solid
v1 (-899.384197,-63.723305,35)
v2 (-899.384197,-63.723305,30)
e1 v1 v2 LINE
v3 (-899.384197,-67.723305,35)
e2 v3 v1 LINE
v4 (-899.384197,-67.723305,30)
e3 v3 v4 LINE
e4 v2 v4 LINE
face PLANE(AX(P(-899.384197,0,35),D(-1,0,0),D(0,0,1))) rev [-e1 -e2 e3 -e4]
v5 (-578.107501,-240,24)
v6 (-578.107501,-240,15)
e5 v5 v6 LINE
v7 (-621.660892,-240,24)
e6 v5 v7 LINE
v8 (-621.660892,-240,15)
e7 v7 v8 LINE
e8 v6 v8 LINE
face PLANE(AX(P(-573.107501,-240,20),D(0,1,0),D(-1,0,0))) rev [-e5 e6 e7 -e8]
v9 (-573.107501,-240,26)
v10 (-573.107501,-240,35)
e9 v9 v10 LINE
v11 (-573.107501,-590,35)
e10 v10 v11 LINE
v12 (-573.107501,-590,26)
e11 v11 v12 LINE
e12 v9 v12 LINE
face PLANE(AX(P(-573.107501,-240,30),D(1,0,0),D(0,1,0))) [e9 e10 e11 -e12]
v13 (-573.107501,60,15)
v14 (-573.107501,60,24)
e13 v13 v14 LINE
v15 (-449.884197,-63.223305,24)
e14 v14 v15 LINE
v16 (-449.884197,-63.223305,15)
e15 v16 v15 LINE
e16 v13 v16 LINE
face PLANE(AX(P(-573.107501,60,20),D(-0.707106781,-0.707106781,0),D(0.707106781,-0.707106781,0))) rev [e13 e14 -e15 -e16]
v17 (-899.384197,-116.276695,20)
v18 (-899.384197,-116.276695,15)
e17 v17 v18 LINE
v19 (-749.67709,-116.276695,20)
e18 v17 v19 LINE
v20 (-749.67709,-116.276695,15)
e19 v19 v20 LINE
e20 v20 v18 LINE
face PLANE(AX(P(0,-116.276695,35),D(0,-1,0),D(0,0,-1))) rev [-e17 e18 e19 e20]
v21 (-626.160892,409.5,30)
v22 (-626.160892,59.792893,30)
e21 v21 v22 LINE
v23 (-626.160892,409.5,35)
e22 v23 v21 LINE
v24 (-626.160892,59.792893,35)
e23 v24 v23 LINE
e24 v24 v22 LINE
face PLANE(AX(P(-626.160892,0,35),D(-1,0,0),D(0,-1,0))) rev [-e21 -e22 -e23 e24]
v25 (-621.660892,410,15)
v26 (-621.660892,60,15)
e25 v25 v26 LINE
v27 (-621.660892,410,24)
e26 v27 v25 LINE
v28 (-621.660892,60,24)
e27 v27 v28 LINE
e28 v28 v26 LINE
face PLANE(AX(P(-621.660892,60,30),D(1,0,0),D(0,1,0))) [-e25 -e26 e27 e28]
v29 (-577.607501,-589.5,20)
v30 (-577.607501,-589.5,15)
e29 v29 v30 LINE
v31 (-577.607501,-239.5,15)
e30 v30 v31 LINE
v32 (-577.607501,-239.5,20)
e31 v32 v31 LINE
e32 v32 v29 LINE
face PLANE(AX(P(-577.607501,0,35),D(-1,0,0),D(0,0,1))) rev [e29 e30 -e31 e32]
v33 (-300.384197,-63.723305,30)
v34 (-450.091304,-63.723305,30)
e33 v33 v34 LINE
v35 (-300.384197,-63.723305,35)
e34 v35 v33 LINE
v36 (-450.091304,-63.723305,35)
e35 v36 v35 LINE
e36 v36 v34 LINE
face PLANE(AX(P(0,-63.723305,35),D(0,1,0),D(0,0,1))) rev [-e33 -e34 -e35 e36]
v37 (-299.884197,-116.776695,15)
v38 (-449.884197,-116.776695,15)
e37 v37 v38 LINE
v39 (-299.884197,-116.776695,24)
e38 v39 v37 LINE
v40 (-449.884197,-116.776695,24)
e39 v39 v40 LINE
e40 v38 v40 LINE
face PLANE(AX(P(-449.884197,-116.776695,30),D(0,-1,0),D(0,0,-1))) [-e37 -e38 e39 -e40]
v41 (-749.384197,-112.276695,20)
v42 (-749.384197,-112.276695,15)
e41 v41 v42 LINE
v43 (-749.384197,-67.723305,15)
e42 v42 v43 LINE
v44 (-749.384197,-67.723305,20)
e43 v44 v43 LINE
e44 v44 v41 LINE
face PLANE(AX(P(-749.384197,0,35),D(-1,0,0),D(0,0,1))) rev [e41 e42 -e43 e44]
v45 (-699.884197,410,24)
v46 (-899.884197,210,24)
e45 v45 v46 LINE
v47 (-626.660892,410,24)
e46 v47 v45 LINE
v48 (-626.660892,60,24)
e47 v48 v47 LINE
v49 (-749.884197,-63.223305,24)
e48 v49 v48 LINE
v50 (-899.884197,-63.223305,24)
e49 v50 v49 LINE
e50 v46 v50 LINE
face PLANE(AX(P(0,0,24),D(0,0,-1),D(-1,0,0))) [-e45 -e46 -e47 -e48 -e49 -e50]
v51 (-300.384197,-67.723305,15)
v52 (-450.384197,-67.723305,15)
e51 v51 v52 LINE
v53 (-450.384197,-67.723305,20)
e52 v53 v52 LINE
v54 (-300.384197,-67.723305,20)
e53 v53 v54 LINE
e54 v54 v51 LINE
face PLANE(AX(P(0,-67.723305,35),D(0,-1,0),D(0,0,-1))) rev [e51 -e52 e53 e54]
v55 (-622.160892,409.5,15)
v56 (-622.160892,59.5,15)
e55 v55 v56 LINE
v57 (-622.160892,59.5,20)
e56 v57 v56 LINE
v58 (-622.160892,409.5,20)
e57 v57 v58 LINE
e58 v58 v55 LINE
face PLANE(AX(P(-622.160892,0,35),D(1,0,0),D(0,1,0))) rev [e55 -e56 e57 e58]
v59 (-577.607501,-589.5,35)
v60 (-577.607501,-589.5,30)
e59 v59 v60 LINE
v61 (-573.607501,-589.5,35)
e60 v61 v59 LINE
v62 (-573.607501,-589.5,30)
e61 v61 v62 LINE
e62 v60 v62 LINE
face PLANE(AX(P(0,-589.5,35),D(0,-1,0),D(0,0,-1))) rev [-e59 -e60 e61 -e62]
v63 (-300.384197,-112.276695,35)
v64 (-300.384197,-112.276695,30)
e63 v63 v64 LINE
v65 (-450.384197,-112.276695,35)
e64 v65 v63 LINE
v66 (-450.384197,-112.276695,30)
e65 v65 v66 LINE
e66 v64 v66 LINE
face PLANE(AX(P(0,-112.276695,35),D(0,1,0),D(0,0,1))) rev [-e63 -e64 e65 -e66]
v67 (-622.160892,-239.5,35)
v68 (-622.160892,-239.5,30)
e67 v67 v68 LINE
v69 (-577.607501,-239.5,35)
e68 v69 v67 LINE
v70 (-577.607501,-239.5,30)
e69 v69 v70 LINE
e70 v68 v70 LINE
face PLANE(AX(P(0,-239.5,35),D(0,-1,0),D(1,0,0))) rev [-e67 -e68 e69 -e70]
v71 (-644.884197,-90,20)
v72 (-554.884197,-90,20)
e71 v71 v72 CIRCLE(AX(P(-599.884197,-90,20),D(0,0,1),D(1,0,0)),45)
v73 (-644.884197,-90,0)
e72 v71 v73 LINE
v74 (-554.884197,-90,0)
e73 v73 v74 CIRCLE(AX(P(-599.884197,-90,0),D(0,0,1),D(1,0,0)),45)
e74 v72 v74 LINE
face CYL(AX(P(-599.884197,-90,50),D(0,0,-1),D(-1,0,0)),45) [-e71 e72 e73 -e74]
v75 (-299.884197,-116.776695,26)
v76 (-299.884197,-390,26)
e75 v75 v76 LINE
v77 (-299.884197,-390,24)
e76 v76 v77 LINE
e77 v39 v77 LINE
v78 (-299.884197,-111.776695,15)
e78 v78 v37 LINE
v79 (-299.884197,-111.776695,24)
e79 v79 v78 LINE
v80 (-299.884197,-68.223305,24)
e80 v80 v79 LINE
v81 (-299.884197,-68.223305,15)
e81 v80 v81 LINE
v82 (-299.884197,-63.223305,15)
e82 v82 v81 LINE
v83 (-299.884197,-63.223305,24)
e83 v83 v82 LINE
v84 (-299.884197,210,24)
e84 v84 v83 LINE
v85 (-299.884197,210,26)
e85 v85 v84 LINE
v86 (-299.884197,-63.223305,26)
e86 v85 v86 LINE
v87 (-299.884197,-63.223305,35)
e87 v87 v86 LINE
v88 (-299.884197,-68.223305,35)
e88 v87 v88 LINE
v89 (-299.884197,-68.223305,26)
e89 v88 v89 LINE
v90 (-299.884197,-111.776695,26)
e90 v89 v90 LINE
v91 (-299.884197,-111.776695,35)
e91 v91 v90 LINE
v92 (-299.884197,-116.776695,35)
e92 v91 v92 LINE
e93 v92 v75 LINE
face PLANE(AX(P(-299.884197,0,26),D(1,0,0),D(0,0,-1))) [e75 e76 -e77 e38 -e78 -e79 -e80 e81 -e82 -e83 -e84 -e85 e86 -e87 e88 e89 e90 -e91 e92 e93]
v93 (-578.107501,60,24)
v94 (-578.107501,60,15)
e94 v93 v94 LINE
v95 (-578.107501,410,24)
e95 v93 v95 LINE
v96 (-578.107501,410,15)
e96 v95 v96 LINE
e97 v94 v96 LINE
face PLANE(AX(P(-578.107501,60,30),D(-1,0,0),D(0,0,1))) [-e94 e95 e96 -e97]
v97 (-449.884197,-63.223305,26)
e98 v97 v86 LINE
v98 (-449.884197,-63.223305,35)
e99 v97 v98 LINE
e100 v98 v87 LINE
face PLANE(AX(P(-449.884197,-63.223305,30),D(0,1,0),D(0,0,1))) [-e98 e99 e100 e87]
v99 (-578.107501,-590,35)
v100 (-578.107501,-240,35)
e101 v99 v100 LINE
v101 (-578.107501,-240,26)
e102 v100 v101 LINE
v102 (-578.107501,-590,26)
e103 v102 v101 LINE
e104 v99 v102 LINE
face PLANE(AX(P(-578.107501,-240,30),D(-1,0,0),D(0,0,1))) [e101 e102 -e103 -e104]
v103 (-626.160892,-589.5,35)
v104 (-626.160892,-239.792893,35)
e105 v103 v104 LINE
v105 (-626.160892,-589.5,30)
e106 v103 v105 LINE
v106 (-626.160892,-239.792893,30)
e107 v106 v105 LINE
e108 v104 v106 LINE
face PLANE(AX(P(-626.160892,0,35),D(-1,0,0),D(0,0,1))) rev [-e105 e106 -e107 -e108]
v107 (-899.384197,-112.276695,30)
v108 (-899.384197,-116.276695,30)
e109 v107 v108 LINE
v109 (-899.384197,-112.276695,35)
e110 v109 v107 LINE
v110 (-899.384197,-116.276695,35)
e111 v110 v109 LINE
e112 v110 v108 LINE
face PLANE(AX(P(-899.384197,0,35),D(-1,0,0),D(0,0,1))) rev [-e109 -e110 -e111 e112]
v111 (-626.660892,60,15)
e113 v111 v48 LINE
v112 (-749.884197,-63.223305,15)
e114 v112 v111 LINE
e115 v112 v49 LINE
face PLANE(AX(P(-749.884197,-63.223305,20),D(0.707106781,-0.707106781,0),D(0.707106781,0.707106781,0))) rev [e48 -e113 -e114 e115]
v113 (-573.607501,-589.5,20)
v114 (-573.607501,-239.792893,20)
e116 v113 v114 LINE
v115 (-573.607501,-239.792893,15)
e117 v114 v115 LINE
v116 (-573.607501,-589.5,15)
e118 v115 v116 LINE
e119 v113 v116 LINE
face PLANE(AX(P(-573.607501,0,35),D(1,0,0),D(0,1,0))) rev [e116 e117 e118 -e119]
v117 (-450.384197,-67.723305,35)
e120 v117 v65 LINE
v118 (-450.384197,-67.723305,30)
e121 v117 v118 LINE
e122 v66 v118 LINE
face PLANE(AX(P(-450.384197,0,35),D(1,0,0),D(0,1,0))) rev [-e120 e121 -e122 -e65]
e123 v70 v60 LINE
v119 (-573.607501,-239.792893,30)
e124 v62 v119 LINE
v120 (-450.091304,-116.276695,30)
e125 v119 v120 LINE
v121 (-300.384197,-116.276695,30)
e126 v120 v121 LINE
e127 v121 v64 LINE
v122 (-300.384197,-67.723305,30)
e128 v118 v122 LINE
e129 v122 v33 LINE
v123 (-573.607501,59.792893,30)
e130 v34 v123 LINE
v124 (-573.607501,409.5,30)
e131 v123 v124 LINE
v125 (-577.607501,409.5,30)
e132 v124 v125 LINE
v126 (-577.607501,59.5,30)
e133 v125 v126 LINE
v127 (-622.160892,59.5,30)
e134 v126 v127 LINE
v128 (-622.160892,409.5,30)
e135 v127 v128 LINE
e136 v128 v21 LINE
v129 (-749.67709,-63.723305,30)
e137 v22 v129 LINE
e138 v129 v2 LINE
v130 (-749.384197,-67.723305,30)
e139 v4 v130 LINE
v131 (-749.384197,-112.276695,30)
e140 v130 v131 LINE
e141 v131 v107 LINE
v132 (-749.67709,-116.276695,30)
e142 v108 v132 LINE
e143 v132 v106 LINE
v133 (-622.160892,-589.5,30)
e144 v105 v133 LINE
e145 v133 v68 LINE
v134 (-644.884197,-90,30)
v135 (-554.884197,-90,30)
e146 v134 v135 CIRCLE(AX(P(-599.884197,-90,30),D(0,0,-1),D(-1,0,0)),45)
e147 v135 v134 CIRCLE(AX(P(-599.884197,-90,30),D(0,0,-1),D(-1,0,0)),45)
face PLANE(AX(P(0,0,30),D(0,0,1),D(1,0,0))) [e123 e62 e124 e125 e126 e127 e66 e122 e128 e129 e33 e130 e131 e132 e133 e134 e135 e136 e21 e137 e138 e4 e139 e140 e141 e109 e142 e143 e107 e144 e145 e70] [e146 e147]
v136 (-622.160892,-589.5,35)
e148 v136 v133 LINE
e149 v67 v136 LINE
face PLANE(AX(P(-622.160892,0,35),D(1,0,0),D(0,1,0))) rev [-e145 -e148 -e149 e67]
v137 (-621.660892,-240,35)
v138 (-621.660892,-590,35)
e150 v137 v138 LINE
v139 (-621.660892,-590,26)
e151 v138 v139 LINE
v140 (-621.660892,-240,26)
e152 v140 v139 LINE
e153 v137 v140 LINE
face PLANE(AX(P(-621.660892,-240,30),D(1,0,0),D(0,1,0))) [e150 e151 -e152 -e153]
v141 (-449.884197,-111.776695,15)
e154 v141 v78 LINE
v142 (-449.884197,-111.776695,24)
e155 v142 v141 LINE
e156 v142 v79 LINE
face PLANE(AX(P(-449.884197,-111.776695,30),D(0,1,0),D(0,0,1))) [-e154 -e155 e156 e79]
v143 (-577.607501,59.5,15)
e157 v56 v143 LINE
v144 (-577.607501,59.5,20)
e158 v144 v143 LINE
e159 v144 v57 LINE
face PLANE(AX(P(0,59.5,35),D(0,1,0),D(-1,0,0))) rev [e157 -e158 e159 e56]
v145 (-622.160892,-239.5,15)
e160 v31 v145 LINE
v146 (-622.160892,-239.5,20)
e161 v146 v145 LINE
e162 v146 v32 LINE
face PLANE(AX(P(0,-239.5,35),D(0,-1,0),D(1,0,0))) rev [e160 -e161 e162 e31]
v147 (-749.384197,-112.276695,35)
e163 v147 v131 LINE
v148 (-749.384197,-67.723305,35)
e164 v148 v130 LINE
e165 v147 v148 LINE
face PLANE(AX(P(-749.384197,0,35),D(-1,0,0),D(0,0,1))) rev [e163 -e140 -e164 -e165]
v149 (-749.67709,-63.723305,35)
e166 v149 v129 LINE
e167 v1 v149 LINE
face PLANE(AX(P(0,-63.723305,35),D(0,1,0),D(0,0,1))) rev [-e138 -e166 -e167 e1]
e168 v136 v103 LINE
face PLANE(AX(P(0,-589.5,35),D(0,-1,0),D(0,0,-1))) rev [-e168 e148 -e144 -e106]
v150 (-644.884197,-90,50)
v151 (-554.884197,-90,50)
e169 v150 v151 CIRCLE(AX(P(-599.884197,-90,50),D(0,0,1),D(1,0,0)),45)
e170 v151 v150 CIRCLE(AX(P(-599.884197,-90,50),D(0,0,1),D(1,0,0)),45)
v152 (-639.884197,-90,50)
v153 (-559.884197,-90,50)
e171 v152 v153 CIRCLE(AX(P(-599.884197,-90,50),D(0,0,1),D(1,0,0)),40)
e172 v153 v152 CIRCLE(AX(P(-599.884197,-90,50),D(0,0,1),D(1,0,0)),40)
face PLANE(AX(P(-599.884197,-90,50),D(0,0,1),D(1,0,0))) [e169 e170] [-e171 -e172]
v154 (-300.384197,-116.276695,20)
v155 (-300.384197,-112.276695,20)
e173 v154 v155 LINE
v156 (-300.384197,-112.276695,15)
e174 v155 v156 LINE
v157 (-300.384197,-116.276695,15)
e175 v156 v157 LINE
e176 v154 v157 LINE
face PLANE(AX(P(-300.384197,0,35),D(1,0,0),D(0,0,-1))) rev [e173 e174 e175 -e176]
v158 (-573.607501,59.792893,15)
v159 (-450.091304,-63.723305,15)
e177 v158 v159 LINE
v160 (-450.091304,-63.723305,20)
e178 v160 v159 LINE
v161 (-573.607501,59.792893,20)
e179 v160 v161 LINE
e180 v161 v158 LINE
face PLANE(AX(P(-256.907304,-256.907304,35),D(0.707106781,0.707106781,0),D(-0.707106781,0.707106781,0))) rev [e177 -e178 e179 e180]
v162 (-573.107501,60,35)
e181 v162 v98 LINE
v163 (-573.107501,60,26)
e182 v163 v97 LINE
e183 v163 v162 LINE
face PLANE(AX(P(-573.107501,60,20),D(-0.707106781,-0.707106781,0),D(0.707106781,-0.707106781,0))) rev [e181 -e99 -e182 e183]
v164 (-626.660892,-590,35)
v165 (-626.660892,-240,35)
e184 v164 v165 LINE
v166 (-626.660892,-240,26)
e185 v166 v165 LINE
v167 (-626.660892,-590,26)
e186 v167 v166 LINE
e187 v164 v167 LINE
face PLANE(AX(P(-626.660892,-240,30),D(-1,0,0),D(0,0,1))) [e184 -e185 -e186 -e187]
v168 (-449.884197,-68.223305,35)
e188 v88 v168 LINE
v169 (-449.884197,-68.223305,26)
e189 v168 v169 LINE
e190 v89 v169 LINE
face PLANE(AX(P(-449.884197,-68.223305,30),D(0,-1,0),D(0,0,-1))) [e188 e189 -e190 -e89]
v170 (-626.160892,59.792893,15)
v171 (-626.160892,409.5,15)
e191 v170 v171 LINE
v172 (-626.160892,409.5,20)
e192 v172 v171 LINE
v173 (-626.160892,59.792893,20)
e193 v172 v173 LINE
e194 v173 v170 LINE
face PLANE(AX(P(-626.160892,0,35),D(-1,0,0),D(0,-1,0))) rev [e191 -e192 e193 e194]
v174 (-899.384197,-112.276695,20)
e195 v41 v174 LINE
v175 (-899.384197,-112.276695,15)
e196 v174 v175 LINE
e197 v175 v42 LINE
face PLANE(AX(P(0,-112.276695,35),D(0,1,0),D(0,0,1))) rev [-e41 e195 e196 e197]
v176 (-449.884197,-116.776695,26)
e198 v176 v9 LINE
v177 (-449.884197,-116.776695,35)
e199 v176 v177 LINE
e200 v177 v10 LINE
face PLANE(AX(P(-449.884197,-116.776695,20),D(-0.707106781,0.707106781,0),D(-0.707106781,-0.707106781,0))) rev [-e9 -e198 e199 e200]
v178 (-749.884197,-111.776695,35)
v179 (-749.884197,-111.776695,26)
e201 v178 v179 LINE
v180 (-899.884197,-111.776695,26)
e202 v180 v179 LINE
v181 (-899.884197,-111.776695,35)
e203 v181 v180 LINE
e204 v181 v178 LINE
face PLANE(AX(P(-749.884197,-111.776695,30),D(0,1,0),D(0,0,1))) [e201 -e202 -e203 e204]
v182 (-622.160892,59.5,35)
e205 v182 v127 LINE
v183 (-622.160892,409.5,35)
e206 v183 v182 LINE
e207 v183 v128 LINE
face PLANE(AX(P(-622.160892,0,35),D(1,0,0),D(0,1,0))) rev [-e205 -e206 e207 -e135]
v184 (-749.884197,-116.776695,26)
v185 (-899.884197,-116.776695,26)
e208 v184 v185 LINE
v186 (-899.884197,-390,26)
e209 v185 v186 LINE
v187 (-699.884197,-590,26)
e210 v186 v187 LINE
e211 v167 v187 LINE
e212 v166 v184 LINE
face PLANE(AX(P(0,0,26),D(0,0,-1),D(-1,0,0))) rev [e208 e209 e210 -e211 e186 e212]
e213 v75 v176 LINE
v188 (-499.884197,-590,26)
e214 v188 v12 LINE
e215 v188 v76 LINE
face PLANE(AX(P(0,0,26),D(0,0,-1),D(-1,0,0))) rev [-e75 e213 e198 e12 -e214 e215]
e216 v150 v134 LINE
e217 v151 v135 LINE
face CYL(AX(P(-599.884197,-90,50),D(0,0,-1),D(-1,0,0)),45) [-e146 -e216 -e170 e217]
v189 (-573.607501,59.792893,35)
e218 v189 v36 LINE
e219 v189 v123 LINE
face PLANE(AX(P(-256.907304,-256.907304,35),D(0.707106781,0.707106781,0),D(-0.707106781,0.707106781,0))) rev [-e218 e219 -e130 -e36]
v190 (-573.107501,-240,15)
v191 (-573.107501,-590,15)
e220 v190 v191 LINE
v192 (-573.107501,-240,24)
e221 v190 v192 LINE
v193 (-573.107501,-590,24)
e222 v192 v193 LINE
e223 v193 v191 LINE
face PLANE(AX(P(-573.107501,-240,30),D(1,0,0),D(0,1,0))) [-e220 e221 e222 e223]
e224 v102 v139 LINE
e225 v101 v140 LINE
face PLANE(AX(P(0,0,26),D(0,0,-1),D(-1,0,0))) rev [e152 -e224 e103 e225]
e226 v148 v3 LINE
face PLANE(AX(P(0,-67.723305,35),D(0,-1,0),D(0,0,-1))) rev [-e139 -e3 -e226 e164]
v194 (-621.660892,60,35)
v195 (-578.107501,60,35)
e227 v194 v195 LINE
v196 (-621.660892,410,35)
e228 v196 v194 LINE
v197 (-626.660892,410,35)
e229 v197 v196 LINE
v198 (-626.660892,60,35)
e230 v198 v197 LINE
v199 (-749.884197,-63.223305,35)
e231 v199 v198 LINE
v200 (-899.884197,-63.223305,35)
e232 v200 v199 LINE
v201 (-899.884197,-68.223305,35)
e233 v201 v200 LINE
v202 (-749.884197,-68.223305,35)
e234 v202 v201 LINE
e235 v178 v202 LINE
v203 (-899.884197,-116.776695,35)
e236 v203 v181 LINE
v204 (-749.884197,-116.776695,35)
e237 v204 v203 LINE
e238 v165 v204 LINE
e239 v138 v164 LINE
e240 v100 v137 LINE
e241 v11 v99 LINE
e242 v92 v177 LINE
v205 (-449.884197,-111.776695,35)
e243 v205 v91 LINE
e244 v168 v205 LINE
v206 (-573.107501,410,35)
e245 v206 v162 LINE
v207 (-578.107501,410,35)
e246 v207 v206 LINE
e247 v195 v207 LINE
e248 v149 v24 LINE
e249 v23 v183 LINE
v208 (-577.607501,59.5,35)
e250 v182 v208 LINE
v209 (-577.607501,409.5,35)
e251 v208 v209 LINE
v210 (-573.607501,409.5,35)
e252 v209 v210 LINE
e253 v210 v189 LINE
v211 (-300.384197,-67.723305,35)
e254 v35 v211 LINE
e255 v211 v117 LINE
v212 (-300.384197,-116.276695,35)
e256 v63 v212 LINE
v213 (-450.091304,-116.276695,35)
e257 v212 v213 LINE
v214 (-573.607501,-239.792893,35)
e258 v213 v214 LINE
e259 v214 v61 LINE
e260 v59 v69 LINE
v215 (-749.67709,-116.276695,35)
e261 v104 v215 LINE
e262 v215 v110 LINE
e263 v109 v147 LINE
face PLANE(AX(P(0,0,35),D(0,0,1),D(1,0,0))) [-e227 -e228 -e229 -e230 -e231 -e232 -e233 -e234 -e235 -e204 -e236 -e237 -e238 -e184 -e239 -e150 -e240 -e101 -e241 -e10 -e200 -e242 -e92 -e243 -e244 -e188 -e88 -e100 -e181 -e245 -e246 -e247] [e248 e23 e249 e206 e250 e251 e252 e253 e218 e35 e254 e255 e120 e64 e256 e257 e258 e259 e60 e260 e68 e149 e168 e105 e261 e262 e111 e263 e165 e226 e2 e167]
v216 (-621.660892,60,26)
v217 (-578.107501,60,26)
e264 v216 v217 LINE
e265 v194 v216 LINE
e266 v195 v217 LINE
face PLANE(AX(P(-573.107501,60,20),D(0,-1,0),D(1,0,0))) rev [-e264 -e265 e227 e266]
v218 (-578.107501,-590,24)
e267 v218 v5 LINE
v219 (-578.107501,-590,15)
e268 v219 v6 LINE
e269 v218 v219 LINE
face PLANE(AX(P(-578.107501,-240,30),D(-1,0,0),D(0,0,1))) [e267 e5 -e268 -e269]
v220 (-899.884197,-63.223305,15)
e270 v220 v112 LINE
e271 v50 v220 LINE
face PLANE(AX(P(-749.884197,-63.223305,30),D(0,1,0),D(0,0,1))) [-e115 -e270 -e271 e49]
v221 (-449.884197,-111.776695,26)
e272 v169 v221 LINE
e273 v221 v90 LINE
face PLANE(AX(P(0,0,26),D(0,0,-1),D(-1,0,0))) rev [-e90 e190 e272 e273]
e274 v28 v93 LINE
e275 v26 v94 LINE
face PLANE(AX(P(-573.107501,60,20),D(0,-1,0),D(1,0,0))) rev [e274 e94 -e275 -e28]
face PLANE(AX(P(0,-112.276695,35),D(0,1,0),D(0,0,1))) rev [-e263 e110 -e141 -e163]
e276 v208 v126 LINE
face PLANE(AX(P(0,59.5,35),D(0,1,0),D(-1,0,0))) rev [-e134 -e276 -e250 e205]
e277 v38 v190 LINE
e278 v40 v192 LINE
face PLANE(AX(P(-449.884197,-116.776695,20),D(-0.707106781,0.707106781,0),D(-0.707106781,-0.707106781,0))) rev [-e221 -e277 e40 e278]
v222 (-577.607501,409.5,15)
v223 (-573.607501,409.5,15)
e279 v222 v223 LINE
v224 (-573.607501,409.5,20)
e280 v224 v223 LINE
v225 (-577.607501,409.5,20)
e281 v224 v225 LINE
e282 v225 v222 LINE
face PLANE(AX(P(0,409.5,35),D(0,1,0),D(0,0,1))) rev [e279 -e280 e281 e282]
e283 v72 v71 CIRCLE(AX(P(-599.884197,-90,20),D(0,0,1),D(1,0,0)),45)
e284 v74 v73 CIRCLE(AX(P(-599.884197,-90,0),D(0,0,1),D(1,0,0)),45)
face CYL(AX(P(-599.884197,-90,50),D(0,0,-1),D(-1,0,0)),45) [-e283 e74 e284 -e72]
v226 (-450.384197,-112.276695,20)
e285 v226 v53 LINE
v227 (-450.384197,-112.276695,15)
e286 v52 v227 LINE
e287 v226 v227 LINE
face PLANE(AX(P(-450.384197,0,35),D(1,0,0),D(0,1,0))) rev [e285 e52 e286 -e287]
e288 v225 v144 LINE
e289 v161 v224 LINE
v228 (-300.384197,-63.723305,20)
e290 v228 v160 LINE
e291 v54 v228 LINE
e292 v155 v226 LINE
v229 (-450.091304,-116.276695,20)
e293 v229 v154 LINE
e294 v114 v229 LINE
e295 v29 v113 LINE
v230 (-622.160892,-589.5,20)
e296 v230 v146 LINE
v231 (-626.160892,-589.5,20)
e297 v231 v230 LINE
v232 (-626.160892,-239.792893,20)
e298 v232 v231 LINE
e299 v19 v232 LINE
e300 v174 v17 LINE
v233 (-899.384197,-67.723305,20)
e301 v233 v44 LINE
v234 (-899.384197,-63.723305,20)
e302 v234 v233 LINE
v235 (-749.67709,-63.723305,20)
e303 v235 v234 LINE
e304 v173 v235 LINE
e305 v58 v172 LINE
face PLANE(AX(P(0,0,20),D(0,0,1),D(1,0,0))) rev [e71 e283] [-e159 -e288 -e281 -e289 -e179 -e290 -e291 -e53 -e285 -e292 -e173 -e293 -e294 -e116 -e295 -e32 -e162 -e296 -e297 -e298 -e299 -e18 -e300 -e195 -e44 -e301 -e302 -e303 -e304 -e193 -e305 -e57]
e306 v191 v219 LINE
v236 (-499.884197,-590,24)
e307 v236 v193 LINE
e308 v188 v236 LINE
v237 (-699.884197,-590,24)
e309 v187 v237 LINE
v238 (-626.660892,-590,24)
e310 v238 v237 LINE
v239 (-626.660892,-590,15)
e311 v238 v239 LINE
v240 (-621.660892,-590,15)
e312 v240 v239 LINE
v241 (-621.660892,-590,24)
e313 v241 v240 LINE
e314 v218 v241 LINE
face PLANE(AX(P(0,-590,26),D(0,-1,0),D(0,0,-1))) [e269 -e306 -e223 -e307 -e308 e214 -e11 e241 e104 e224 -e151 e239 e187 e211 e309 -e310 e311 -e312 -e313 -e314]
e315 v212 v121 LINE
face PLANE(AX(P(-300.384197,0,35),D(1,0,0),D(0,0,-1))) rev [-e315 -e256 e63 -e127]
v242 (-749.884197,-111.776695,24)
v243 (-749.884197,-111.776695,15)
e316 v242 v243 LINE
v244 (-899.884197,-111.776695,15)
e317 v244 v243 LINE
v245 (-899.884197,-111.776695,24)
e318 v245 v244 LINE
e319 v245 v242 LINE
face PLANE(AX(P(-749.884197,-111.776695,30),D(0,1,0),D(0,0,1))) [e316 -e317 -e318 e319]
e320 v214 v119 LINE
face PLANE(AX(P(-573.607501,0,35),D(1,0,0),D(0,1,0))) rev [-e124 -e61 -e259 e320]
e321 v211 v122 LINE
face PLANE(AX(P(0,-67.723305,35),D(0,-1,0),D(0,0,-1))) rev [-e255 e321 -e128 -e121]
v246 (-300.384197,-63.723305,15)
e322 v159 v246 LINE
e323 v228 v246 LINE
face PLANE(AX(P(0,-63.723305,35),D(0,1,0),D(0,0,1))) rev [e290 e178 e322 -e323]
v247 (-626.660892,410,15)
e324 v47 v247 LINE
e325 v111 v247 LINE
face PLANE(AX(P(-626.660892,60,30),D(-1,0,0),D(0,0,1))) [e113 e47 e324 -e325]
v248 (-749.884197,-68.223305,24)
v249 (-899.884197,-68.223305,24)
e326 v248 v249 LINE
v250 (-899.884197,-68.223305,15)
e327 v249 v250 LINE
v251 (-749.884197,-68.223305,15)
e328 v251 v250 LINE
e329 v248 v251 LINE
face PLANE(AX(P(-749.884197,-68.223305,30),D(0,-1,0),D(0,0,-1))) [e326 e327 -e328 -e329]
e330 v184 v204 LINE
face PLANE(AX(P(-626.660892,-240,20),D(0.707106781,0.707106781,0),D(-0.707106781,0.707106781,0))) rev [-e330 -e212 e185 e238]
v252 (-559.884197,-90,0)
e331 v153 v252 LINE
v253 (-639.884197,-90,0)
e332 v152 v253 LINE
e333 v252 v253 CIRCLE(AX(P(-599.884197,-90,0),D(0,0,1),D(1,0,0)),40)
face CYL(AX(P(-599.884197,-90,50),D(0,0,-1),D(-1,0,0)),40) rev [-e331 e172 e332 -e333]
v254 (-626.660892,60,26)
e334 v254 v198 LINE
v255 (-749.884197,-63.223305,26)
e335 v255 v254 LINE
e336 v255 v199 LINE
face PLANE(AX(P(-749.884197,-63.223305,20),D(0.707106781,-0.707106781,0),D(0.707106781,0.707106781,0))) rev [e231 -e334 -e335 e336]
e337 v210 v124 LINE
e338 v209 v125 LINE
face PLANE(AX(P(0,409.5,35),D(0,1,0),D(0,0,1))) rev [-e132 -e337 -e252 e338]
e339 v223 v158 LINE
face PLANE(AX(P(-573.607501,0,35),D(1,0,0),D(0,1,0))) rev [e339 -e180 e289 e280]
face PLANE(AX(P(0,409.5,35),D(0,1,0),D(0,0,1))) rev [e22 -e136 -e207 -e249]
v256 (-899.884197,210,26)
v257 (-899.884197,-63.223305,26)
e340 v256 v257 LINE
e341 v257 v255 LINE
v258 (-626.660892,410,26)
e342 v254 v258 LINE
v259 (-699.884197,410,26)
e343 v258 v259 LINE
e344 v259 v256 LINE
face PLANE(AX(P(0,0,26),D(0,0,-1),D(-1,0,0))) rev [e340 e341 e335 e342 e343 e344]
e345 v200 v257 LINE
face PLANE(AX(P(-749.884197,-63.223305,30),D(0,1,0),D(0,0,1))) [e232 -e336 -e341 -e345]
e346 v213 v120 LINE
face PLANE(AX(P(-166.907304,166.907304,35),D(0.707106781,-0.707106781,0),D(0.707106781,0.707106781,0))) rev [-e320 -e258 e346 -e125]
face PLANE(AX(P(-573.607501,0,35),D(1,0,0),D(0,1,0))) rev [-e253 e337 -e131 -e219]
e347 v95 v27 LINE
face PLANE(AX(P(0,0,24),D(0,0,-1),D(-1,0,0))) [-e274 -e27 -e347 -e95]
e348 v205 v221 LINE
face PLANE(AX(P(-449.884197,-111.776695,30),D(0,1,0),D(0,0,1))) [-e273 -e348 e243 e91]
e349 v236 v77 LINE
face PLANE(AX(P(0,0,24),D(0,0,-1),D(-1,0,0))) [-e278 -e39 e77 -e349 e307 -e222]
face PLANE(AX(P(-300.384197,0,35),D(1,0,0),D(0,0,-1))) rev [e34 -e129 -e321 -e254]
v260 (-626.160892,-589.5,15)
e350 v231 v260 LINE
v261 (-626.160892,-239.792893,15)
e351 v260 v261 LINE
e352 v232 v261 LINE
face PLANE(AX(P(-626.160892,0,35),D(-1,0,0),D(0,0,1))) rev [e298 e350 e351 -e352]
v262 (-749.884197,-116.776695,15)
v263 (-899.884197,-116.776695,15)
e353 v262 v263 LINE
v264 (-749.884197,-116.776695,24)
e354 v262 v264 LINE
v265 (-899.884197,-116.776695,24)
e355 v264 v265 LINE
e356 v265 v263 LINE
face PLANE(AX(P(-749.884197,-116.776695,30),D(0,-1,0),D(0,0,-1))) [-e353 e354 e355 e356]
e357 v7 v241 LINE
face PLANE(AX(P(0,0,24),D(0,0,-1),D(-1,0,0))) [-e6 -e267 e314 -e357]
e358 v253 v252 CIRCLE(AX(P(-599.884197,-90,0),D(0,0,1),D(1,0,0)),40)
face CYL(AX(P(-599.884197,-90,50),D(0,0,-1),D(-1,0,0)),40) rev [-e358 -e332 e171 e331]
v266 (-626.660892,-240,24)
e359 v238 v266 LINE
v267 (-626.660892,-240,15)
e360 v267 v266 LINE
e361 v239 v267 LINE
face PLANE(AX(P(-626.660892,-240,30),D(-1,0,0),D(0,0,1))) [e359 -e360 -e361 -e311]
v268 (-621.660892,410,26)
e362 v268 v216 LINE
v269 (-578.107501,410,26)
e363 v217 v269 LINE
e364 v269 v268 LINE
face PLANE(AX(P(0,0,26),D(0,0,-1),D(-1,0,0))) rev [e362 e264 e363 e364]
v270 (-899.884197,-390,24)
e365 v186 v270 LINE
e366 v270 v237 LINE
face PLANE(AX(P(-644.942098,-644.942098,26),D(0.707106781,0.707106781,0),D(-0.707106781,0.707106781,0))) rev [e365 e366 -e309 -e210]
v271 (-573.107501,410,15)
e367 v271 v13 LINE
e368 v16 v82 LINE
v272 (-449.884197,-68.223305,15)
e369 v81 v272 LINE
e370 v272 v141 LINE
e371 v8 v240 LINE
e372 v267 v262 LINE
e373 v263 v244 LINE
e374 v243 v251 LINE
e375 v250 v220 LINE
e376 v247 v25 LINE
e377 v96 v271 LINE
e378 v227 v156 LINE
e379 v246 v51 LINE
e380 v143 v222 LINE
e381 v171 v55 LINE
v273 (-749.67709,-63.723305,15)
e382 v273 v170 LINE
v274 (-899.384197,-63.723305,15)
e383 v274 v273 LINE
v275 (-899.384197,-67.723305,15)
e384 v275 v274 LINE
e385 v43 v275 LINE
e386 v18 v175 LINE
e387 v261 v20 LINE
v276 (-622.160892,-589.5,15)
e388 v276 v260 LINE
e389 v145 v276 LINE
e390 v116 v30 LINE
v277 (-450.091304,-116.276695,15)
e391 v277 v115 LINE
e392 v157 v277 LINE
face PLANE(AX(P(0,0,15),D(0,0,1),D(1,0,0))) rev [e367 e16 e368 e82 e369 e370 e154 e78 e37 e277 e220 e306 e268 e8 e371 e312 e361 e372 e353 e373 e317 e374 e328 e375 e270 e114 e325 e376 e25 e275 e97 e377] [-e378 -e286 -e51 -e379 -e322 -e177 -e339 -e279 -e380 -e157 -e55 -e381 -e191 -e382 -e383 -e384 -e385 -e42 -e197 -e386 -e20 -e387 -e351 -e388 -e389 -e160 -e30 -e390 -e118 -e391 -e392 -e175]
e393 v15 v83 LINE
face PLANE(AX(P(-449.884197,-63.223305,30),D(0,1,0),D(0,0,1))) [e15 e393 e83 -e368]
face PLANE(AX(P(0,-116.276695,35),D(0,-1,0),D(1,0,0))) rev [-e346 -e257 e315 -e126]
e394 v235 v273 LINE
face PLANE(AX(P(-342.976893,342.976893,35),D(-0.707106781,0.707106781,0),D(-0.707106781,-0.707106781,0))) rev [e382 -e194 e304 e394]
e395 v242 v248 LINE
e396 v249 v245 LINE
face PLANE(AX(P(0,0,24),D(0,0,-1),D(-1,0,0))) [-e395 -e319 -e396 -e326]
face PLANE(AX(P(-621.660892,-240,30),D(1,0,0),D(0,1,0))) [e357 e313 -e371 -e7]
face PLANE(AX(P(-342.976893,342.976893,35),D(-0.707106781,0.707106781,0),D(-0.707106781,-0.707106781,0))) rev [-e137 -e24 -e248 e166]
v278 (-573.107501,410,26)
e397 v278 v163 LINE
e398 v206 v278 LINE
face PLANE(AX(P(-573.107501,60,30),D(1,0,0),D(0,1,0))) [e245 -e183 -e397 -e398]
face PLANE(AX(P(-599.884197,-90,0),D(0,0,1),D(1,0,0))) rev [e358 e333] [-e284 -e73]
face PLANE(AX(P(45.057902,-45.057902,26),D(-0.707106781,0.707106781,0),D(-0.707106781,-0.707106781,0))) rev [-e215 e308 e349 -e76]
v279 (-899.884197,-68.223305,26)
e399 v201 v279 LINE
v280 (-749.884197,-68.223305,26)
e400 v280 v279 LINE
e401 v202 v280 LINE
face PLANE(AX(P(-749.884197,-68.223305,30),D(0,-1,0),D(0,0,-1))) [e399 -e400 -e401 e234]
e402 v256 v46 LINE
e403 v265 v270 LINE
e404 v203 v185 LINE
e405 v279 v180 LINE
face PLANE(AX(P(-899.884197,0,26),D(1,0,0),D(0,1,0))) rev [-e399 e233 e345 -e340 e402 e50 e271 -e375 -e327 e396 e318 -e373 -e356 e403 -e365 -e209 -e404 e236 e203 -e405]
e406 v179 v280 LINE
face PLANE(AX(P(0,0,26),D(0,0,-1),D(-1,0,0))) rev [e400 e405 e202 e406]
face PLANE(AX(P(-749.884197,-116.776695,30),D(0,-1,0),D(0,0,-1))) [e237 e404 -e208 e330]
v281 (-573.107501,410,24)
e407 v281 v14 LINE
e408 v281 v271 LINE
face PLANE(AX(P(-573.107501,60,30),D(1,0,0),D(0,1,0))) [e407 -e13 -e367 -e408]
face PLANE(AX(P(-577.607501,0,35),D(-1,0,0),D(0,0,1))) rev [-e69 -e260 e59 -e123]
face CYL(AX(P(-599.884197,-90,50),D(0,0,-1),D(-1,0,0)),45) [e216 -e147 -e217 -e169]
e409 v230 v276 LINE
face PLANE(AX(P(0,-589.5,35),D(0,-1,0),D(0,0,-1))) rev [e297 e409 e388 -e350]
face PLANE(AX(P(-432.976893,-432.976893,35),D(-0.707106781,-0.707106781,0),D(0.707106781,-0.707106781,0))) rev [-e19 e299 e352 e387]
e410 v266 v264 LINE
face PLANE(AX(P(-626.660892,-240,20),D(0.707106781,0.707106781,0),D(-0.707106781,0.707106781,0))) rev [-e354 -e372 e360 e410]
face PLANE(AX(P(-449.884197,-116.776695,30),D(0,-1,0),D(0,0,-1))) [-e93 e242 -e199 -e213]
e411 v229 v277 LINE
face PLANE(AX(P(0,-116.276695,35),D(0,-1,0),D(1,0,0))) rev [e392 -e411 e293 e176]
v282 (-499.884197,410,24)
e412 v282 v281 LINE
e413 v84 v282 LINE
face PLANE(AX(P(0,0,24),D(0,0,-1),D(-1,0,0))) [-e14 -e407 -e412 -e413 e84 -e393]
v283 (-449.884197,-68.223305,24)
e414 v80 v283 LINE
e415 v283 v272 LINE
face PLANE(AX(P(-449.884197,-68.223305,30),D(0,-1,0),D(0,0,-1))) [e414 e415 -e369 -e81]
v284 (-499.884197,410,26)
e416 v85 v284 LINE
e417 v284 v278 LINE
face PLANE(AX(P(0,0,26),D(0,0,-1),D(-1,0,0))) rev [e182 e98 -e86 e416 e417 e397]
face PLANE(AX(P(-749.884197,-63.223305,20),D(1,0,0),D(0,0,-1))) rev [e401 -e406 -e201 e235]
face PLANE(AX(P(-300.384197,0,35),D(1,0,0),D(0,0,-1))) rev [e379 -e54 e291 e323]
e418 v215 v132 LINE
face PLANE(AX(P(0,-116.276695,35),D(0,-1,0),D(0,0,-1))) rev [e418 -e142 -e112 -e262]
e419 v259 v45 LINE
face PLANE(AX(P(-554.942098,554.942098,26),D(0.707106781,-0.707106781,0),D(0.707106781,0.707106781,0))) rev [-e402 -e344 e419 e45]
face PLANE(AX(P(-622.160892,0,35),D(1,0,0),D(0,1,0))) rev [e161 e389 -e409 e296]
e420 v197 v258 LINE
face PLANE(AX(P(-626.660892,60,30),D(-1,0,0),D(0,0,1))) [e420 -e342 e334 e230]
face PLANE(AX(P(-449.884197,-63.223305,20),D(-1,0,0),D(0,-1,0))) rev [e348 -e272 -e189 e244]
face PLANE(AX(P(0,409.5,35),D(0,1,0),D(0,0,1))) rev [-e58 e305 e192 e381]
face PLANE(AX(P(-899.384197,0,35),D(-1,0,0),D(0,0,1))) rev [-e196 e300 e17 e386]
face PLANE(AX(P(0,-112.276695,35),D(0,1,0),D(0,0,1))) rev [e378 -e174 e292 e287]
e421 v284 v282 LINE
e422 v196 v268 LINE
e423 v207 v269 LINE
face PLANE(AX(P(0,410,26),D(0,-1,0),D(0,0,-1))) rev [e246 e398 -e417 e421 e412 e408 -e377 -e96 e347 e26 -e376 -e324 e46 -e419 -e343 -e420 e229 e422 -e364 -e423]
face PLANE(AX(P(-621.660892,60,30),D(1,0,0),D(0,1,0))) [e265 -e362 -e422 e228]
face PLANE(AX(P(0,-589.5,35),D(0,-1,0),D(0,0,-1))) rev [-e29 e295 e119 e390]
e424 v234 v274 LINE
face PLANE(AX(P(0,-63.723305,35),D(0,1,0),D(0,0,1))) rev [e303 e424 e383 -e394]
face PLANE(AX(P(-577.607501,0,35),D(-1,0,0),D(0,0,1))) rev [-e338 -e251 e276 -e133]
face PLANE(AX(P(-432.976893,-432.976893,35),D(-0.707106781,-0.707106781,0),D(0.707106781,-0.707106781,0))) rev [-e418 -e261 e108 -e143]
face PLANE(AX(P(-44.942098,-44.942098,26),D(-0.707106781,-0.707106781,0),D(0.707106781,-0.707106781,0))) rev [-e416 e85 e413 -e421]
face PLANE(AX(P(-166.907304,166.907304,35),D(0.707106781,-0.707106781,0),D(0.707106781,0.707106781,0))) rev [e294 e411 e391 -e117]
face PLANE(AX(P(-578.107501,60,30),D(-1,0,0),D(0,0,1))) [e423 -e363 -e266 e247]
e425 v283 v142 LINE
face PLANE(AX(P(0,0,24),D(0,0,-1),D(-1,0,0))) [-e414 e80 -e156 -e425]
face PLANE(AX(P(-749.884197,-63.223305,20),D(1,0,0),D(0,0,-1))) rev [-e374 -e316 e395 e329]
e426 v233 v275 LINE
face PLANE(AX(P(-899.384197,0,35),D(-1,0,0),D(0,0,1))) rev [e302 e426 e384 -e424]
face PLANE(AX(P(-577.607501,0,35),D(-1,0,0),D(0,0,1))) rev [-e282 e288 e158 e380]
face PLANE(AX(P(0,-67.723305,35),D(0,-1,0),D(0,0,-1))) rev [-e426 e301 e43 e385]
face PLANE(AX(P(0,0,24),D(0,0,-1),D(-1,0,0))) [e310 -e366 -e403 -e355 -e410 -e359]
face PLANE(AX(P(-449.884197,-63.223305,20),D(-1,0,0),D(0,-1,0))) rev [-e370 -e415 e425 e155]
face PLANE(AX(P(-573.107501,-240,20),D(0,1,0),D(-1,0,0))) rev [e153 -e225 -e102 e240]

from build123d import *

# Parameters (mm, degrees)
SKETCH1_R                = 45
SKETCH1_R_2              = 40
BOSS_EXTRUDE1_DEPTH      = 50
BOSS_EXTRUDE2_START      = 10
SKETCH4_R                = 45
BOSS_EXTRUDE2_DEPTH      = 10
BOSS_EXTRUDE3_START      = -4
SKETCH6_W                = 200
SKETCH6_H                = 600
SKETCH6_H_2              = 200
SKETCH6_R                = 40
BOSS_EXTRUDE3_DEPTH      = 2
SKETCH7_W                = 150
SKETCH7_H                = 5
SKETCH7_W_2              = 5
SKETCH7_H_2              = 350
BOSS_EXTRUDE4_DEPTH      = 10
EXTRUDE_THIN2_DEPTH      = 5
EXTRUDE_THIN2_DEPTH_BACK = 15


with BuildPart() as part:
    # Sketch1 → Boss-Extrude1 (new body)
    with BuildSketch(Plane.XY):
        with Locations((-599.884196758, -90)):
            Circle(SKETCH1_R)
        with Locations((-599.884196758, -90)):
            Circle(SKETCH1_R_2, mode=Mode.SUBTRACT)
    extrude(amount=BOSS_EXTRUDE1_DEPTH)

    # Sketch4 → Boss-Extrude2 (add)
    with BuildSketch(Plane(origin=(0, 0, 30), x_dir=(-1, 0, 0), z_dir=(0, 0, -1)).offset(BOSS_EXTRUDE2_START)):
        Polygon((626.660892055, -240), (749.884196758, -116.776695297), (749.884196758, -63.223304703), (626.660892055, 60), (573.107501461, 60), (449.884196758, -63.223304703), (449.884196758, -116.776695297), (573.107501461, -240), align=None)
        with Locations(Location((599.884196758, -90, 0), (0, 0, 180))):
            Circle(SKETCH4_R, mode=Mode.SUBTRACT)
    extrude(amount=-BOSS_EXTRUDE2_DEPTH)

    # Sketch6 → Boss-Extrude3 (add)
    # profile 1 of 9: a face of its own
    with BuildSketch(Plane(origin=(0, 0, 20), x_dir=(-1, 0, 0), z_dir=(0, 0, -1)).offset(BOSS_EXTRUDE3_START)):
        with Locations((799.884196758, -90)):
            Rectangle(SKETCH6_W, SKETCH6_H)
    # profile 2 of 9: a face of its own
    with BuildSketch(Plane(origin=(0, 0, 20), x_dir=(-1, 0, 0), z_dir=(0, 0, -1)).offset(BOSS_EXTRUDE3_START)):
        Polygon((699.884196758, -590), (899.884196758, -390), (699.884196758, -390), align=None)
    # profile 3 of 9: a face of its own
    with BuildSketch(Plane(origin=(0, 0, 20), x_dir=(-1, 0, 0), z_dir=(0, 0, -1)).offset(BOSS_EXTRUDE3_START)):
        with Locations((599.884196758, -490)):
            Rectangle(SKETCH6_W, SKETCH6_H_2)
    # profile 4 of 9: a face of its own
    with BuildSketch(Plane(origin=(0, 0, 20), x_dir=(-1, 0, 0), z_dir=(0, 0, -1)).offset(BOSS_EXTRUDE3_START)):
        Polygon((699.884196758, 210), (899.884196758, 210), (699.884196758, 410), align=None)
    # profile 5 of 9: a face of its own
    with BuildSketch(Plane(origin=(0, 0, 20), x_dir=(-1, 0, 0), z_dir=(0, 0, -1)).offset(BOSS_EXTRUDE3_START)):
        with Locations((599.884196758, -90)):
            Rectangle(SKETCH6_W, SKETCH6_H)
        with Locations(Location((599.884196758, -90, 0), (0, 0, 180))):
            Circle(SKETCH6_R, mode=Mode.SUBTRACT)
    # profile 6 of 9: a face of its own
    with BuildSketch(Plane(origin=(0, 0, 20), x_dir=(-1, 0, 0), z_dir=(0, 0, -1)).offset(BOSS_EXTRUDE3_START)):
        Polygon((299.884196758, -390), (499.884196758, -590), (499.884196758, -390), align=None)
    # profile 7 of 9: a face of its own
    with BuildSketch(Plane(origin=(0, 0, 20), x_dir=(-1, 0, 0), z_dir=(0, 0, -1)).offset(BOSS_EXTRUDE3_START)):
        with Locations((599.884196758, 310)):
            Rectangle(SKETCH6_W, SKETCH6_H_2)
    # profile 8 of 9: a face of its own
    with BuildSketch(Plane(origin=(0, 0, 20), x_dir=(-1, 0, 0), z_dir=(0, 0, -1)).offset(BOSS_EXTRUDE3_START)):
        with Locations((399.884196758, -90)):
            Rectangle(SKETCH6_W, SKETCH6_H)
    # profile 9 of 9: a face of its own
    with BuildSketch(Plane(origin=(0, 0, 20), x_dir=(-1, 0, 0), z_dir=(0, 0, -1)).offset(BOSS_EXTRUDE3_START)):
        Polygon((299.884196758, 210), (499.884196758, 210), (499.884196758, 410), align=None)
    extrude(amount=-BOSS_EXTRUDE3_DEPTH)

    # Sketch7 → Boss-Extrude4 (add)
    with BuildSketch(Plane(origin=(0, 0, 20), x_dir=(-1, 0, 0), z_dir=(0, 0, -1))):
        with Locations((824.884196758, -65.723304703)):
            Rectangle(SKETCH7_W, SKETCH7_H)
        with Locations((824.884196758, -114.276695297)):
            Rectangle(SKETCH7_W, SKETCH7_H)
        with Locations((374.884196758, -114.276695297)):
            Rectangle(SKETCH7_W, SKETCH7_H)
        with Locations((374.884196758, -65.723304703)):
            Rectangle(SKETCH7_W, SKETCH7_H)
        with Locations((624.160892055, -415)):
            Rectangle(SKETCH7_W_2, SKETCH7_H_2)
        with Locations((575.607501461, -415)):
            Rectangle(SKETCH7_W_2, SKETCH7_H_2)
        with Locations((575.607501461, 235)):
            Rectangle(SKETCH7_W_2, SKETCH7_H_2)
        with Locations((624.160892055, 235)):
            Rectangle(SKETCH7_W_2, SKETCH7_H_2)
    extrude(amount=-BOSS_EXTRUDE4_DEPTH)

    # Sketch8 → Extrude-Thin2 (add, two sides: drawn at the far end of the back side and taken through both)
    with BuildSketch(Plane(origin=(0, 0, 20), x_dir=(-1, 0, 0), z_dir=(0, 0, -1)).offset(-EXTRUDE_THIN2_DEPTH_BACK)):
        Polygon((749.884196758, -63.223304703), (626.660892055, 60), (626.660892055, 410), (621.660892055, 410), (621.660892055, 60), (578.107501461, 60), (578.107501461, 410), (573.107501461, 410), (573.107501461, 60), (449.884196758, -63.223304703), (299.884196758, -63.223304703), (299.884196758, -68.223304703), (449.884196758, -68.223304703), (449.884196758, -111.776695297), (299.884196758, -111.776695297), (299.884196758, -116.776695297), (449.884196758, -116.776695297), (573.107501461, -240), (573.107501461, -590), (578.107501461, -590), (578.107501461, -240), (621.660892055, -240), (621.660892055, -590), (626.660892055, -590), (626.660892055, -240), (749.884196758, -116.776695297), (899.884196758, -116.776695297), (899.884196758, -111.776695297), (749.884196758, -111.776695297), (749.884196758, -68.223304703), (899.884196758, -68.223304703), (899.884196758, -63.223304703), align=None)
        Polygon((749.677089977, -63.723304703), (626.160892055, 59.792893219), (626.160892055, 409.5), (622.160892055, 409.5), (622.160892055, 59.5), (577.607501461, 59.5), (577.607501461, 409.5), (573.607501461, 409.5), (573.607501461, 59.792893219), (450.091303539, -63.723304703), (300.384196758, -63.723304703), (300.384196758, -67.723304703), (450.384196758, -67.723304703), (450.384196758, -112.276695297), (300.384196758, -112.276695297), (300.384196758, -116.276695297), (450.091303539, -116.276695297), (573.607501461, -239.792893219), (573.607501461, -589.5), (577.607501461, -589.5), (577.607501461, -239.5), (622.160892055, -239.5), (622.160892055, -589.5), (626.160892055, -589.5), (626.160892055, -239.792893219), (749.677089977, -116.276695297), (899.384196758, -116.276695297), (899.384196758, -112.276695297), (749.384196758, -112.276695297), (749.384196758, -67.723304703), (899.384196758, -67.723304703), (899.384196758, -63.723304703), align=None, mode=Mode.SUBTRACT)
    extrude(amount=EXTRUDE_THIN2_DEPTH + EXTRUDE_THIN2_DEPTH_BACK)


solid = part.part
